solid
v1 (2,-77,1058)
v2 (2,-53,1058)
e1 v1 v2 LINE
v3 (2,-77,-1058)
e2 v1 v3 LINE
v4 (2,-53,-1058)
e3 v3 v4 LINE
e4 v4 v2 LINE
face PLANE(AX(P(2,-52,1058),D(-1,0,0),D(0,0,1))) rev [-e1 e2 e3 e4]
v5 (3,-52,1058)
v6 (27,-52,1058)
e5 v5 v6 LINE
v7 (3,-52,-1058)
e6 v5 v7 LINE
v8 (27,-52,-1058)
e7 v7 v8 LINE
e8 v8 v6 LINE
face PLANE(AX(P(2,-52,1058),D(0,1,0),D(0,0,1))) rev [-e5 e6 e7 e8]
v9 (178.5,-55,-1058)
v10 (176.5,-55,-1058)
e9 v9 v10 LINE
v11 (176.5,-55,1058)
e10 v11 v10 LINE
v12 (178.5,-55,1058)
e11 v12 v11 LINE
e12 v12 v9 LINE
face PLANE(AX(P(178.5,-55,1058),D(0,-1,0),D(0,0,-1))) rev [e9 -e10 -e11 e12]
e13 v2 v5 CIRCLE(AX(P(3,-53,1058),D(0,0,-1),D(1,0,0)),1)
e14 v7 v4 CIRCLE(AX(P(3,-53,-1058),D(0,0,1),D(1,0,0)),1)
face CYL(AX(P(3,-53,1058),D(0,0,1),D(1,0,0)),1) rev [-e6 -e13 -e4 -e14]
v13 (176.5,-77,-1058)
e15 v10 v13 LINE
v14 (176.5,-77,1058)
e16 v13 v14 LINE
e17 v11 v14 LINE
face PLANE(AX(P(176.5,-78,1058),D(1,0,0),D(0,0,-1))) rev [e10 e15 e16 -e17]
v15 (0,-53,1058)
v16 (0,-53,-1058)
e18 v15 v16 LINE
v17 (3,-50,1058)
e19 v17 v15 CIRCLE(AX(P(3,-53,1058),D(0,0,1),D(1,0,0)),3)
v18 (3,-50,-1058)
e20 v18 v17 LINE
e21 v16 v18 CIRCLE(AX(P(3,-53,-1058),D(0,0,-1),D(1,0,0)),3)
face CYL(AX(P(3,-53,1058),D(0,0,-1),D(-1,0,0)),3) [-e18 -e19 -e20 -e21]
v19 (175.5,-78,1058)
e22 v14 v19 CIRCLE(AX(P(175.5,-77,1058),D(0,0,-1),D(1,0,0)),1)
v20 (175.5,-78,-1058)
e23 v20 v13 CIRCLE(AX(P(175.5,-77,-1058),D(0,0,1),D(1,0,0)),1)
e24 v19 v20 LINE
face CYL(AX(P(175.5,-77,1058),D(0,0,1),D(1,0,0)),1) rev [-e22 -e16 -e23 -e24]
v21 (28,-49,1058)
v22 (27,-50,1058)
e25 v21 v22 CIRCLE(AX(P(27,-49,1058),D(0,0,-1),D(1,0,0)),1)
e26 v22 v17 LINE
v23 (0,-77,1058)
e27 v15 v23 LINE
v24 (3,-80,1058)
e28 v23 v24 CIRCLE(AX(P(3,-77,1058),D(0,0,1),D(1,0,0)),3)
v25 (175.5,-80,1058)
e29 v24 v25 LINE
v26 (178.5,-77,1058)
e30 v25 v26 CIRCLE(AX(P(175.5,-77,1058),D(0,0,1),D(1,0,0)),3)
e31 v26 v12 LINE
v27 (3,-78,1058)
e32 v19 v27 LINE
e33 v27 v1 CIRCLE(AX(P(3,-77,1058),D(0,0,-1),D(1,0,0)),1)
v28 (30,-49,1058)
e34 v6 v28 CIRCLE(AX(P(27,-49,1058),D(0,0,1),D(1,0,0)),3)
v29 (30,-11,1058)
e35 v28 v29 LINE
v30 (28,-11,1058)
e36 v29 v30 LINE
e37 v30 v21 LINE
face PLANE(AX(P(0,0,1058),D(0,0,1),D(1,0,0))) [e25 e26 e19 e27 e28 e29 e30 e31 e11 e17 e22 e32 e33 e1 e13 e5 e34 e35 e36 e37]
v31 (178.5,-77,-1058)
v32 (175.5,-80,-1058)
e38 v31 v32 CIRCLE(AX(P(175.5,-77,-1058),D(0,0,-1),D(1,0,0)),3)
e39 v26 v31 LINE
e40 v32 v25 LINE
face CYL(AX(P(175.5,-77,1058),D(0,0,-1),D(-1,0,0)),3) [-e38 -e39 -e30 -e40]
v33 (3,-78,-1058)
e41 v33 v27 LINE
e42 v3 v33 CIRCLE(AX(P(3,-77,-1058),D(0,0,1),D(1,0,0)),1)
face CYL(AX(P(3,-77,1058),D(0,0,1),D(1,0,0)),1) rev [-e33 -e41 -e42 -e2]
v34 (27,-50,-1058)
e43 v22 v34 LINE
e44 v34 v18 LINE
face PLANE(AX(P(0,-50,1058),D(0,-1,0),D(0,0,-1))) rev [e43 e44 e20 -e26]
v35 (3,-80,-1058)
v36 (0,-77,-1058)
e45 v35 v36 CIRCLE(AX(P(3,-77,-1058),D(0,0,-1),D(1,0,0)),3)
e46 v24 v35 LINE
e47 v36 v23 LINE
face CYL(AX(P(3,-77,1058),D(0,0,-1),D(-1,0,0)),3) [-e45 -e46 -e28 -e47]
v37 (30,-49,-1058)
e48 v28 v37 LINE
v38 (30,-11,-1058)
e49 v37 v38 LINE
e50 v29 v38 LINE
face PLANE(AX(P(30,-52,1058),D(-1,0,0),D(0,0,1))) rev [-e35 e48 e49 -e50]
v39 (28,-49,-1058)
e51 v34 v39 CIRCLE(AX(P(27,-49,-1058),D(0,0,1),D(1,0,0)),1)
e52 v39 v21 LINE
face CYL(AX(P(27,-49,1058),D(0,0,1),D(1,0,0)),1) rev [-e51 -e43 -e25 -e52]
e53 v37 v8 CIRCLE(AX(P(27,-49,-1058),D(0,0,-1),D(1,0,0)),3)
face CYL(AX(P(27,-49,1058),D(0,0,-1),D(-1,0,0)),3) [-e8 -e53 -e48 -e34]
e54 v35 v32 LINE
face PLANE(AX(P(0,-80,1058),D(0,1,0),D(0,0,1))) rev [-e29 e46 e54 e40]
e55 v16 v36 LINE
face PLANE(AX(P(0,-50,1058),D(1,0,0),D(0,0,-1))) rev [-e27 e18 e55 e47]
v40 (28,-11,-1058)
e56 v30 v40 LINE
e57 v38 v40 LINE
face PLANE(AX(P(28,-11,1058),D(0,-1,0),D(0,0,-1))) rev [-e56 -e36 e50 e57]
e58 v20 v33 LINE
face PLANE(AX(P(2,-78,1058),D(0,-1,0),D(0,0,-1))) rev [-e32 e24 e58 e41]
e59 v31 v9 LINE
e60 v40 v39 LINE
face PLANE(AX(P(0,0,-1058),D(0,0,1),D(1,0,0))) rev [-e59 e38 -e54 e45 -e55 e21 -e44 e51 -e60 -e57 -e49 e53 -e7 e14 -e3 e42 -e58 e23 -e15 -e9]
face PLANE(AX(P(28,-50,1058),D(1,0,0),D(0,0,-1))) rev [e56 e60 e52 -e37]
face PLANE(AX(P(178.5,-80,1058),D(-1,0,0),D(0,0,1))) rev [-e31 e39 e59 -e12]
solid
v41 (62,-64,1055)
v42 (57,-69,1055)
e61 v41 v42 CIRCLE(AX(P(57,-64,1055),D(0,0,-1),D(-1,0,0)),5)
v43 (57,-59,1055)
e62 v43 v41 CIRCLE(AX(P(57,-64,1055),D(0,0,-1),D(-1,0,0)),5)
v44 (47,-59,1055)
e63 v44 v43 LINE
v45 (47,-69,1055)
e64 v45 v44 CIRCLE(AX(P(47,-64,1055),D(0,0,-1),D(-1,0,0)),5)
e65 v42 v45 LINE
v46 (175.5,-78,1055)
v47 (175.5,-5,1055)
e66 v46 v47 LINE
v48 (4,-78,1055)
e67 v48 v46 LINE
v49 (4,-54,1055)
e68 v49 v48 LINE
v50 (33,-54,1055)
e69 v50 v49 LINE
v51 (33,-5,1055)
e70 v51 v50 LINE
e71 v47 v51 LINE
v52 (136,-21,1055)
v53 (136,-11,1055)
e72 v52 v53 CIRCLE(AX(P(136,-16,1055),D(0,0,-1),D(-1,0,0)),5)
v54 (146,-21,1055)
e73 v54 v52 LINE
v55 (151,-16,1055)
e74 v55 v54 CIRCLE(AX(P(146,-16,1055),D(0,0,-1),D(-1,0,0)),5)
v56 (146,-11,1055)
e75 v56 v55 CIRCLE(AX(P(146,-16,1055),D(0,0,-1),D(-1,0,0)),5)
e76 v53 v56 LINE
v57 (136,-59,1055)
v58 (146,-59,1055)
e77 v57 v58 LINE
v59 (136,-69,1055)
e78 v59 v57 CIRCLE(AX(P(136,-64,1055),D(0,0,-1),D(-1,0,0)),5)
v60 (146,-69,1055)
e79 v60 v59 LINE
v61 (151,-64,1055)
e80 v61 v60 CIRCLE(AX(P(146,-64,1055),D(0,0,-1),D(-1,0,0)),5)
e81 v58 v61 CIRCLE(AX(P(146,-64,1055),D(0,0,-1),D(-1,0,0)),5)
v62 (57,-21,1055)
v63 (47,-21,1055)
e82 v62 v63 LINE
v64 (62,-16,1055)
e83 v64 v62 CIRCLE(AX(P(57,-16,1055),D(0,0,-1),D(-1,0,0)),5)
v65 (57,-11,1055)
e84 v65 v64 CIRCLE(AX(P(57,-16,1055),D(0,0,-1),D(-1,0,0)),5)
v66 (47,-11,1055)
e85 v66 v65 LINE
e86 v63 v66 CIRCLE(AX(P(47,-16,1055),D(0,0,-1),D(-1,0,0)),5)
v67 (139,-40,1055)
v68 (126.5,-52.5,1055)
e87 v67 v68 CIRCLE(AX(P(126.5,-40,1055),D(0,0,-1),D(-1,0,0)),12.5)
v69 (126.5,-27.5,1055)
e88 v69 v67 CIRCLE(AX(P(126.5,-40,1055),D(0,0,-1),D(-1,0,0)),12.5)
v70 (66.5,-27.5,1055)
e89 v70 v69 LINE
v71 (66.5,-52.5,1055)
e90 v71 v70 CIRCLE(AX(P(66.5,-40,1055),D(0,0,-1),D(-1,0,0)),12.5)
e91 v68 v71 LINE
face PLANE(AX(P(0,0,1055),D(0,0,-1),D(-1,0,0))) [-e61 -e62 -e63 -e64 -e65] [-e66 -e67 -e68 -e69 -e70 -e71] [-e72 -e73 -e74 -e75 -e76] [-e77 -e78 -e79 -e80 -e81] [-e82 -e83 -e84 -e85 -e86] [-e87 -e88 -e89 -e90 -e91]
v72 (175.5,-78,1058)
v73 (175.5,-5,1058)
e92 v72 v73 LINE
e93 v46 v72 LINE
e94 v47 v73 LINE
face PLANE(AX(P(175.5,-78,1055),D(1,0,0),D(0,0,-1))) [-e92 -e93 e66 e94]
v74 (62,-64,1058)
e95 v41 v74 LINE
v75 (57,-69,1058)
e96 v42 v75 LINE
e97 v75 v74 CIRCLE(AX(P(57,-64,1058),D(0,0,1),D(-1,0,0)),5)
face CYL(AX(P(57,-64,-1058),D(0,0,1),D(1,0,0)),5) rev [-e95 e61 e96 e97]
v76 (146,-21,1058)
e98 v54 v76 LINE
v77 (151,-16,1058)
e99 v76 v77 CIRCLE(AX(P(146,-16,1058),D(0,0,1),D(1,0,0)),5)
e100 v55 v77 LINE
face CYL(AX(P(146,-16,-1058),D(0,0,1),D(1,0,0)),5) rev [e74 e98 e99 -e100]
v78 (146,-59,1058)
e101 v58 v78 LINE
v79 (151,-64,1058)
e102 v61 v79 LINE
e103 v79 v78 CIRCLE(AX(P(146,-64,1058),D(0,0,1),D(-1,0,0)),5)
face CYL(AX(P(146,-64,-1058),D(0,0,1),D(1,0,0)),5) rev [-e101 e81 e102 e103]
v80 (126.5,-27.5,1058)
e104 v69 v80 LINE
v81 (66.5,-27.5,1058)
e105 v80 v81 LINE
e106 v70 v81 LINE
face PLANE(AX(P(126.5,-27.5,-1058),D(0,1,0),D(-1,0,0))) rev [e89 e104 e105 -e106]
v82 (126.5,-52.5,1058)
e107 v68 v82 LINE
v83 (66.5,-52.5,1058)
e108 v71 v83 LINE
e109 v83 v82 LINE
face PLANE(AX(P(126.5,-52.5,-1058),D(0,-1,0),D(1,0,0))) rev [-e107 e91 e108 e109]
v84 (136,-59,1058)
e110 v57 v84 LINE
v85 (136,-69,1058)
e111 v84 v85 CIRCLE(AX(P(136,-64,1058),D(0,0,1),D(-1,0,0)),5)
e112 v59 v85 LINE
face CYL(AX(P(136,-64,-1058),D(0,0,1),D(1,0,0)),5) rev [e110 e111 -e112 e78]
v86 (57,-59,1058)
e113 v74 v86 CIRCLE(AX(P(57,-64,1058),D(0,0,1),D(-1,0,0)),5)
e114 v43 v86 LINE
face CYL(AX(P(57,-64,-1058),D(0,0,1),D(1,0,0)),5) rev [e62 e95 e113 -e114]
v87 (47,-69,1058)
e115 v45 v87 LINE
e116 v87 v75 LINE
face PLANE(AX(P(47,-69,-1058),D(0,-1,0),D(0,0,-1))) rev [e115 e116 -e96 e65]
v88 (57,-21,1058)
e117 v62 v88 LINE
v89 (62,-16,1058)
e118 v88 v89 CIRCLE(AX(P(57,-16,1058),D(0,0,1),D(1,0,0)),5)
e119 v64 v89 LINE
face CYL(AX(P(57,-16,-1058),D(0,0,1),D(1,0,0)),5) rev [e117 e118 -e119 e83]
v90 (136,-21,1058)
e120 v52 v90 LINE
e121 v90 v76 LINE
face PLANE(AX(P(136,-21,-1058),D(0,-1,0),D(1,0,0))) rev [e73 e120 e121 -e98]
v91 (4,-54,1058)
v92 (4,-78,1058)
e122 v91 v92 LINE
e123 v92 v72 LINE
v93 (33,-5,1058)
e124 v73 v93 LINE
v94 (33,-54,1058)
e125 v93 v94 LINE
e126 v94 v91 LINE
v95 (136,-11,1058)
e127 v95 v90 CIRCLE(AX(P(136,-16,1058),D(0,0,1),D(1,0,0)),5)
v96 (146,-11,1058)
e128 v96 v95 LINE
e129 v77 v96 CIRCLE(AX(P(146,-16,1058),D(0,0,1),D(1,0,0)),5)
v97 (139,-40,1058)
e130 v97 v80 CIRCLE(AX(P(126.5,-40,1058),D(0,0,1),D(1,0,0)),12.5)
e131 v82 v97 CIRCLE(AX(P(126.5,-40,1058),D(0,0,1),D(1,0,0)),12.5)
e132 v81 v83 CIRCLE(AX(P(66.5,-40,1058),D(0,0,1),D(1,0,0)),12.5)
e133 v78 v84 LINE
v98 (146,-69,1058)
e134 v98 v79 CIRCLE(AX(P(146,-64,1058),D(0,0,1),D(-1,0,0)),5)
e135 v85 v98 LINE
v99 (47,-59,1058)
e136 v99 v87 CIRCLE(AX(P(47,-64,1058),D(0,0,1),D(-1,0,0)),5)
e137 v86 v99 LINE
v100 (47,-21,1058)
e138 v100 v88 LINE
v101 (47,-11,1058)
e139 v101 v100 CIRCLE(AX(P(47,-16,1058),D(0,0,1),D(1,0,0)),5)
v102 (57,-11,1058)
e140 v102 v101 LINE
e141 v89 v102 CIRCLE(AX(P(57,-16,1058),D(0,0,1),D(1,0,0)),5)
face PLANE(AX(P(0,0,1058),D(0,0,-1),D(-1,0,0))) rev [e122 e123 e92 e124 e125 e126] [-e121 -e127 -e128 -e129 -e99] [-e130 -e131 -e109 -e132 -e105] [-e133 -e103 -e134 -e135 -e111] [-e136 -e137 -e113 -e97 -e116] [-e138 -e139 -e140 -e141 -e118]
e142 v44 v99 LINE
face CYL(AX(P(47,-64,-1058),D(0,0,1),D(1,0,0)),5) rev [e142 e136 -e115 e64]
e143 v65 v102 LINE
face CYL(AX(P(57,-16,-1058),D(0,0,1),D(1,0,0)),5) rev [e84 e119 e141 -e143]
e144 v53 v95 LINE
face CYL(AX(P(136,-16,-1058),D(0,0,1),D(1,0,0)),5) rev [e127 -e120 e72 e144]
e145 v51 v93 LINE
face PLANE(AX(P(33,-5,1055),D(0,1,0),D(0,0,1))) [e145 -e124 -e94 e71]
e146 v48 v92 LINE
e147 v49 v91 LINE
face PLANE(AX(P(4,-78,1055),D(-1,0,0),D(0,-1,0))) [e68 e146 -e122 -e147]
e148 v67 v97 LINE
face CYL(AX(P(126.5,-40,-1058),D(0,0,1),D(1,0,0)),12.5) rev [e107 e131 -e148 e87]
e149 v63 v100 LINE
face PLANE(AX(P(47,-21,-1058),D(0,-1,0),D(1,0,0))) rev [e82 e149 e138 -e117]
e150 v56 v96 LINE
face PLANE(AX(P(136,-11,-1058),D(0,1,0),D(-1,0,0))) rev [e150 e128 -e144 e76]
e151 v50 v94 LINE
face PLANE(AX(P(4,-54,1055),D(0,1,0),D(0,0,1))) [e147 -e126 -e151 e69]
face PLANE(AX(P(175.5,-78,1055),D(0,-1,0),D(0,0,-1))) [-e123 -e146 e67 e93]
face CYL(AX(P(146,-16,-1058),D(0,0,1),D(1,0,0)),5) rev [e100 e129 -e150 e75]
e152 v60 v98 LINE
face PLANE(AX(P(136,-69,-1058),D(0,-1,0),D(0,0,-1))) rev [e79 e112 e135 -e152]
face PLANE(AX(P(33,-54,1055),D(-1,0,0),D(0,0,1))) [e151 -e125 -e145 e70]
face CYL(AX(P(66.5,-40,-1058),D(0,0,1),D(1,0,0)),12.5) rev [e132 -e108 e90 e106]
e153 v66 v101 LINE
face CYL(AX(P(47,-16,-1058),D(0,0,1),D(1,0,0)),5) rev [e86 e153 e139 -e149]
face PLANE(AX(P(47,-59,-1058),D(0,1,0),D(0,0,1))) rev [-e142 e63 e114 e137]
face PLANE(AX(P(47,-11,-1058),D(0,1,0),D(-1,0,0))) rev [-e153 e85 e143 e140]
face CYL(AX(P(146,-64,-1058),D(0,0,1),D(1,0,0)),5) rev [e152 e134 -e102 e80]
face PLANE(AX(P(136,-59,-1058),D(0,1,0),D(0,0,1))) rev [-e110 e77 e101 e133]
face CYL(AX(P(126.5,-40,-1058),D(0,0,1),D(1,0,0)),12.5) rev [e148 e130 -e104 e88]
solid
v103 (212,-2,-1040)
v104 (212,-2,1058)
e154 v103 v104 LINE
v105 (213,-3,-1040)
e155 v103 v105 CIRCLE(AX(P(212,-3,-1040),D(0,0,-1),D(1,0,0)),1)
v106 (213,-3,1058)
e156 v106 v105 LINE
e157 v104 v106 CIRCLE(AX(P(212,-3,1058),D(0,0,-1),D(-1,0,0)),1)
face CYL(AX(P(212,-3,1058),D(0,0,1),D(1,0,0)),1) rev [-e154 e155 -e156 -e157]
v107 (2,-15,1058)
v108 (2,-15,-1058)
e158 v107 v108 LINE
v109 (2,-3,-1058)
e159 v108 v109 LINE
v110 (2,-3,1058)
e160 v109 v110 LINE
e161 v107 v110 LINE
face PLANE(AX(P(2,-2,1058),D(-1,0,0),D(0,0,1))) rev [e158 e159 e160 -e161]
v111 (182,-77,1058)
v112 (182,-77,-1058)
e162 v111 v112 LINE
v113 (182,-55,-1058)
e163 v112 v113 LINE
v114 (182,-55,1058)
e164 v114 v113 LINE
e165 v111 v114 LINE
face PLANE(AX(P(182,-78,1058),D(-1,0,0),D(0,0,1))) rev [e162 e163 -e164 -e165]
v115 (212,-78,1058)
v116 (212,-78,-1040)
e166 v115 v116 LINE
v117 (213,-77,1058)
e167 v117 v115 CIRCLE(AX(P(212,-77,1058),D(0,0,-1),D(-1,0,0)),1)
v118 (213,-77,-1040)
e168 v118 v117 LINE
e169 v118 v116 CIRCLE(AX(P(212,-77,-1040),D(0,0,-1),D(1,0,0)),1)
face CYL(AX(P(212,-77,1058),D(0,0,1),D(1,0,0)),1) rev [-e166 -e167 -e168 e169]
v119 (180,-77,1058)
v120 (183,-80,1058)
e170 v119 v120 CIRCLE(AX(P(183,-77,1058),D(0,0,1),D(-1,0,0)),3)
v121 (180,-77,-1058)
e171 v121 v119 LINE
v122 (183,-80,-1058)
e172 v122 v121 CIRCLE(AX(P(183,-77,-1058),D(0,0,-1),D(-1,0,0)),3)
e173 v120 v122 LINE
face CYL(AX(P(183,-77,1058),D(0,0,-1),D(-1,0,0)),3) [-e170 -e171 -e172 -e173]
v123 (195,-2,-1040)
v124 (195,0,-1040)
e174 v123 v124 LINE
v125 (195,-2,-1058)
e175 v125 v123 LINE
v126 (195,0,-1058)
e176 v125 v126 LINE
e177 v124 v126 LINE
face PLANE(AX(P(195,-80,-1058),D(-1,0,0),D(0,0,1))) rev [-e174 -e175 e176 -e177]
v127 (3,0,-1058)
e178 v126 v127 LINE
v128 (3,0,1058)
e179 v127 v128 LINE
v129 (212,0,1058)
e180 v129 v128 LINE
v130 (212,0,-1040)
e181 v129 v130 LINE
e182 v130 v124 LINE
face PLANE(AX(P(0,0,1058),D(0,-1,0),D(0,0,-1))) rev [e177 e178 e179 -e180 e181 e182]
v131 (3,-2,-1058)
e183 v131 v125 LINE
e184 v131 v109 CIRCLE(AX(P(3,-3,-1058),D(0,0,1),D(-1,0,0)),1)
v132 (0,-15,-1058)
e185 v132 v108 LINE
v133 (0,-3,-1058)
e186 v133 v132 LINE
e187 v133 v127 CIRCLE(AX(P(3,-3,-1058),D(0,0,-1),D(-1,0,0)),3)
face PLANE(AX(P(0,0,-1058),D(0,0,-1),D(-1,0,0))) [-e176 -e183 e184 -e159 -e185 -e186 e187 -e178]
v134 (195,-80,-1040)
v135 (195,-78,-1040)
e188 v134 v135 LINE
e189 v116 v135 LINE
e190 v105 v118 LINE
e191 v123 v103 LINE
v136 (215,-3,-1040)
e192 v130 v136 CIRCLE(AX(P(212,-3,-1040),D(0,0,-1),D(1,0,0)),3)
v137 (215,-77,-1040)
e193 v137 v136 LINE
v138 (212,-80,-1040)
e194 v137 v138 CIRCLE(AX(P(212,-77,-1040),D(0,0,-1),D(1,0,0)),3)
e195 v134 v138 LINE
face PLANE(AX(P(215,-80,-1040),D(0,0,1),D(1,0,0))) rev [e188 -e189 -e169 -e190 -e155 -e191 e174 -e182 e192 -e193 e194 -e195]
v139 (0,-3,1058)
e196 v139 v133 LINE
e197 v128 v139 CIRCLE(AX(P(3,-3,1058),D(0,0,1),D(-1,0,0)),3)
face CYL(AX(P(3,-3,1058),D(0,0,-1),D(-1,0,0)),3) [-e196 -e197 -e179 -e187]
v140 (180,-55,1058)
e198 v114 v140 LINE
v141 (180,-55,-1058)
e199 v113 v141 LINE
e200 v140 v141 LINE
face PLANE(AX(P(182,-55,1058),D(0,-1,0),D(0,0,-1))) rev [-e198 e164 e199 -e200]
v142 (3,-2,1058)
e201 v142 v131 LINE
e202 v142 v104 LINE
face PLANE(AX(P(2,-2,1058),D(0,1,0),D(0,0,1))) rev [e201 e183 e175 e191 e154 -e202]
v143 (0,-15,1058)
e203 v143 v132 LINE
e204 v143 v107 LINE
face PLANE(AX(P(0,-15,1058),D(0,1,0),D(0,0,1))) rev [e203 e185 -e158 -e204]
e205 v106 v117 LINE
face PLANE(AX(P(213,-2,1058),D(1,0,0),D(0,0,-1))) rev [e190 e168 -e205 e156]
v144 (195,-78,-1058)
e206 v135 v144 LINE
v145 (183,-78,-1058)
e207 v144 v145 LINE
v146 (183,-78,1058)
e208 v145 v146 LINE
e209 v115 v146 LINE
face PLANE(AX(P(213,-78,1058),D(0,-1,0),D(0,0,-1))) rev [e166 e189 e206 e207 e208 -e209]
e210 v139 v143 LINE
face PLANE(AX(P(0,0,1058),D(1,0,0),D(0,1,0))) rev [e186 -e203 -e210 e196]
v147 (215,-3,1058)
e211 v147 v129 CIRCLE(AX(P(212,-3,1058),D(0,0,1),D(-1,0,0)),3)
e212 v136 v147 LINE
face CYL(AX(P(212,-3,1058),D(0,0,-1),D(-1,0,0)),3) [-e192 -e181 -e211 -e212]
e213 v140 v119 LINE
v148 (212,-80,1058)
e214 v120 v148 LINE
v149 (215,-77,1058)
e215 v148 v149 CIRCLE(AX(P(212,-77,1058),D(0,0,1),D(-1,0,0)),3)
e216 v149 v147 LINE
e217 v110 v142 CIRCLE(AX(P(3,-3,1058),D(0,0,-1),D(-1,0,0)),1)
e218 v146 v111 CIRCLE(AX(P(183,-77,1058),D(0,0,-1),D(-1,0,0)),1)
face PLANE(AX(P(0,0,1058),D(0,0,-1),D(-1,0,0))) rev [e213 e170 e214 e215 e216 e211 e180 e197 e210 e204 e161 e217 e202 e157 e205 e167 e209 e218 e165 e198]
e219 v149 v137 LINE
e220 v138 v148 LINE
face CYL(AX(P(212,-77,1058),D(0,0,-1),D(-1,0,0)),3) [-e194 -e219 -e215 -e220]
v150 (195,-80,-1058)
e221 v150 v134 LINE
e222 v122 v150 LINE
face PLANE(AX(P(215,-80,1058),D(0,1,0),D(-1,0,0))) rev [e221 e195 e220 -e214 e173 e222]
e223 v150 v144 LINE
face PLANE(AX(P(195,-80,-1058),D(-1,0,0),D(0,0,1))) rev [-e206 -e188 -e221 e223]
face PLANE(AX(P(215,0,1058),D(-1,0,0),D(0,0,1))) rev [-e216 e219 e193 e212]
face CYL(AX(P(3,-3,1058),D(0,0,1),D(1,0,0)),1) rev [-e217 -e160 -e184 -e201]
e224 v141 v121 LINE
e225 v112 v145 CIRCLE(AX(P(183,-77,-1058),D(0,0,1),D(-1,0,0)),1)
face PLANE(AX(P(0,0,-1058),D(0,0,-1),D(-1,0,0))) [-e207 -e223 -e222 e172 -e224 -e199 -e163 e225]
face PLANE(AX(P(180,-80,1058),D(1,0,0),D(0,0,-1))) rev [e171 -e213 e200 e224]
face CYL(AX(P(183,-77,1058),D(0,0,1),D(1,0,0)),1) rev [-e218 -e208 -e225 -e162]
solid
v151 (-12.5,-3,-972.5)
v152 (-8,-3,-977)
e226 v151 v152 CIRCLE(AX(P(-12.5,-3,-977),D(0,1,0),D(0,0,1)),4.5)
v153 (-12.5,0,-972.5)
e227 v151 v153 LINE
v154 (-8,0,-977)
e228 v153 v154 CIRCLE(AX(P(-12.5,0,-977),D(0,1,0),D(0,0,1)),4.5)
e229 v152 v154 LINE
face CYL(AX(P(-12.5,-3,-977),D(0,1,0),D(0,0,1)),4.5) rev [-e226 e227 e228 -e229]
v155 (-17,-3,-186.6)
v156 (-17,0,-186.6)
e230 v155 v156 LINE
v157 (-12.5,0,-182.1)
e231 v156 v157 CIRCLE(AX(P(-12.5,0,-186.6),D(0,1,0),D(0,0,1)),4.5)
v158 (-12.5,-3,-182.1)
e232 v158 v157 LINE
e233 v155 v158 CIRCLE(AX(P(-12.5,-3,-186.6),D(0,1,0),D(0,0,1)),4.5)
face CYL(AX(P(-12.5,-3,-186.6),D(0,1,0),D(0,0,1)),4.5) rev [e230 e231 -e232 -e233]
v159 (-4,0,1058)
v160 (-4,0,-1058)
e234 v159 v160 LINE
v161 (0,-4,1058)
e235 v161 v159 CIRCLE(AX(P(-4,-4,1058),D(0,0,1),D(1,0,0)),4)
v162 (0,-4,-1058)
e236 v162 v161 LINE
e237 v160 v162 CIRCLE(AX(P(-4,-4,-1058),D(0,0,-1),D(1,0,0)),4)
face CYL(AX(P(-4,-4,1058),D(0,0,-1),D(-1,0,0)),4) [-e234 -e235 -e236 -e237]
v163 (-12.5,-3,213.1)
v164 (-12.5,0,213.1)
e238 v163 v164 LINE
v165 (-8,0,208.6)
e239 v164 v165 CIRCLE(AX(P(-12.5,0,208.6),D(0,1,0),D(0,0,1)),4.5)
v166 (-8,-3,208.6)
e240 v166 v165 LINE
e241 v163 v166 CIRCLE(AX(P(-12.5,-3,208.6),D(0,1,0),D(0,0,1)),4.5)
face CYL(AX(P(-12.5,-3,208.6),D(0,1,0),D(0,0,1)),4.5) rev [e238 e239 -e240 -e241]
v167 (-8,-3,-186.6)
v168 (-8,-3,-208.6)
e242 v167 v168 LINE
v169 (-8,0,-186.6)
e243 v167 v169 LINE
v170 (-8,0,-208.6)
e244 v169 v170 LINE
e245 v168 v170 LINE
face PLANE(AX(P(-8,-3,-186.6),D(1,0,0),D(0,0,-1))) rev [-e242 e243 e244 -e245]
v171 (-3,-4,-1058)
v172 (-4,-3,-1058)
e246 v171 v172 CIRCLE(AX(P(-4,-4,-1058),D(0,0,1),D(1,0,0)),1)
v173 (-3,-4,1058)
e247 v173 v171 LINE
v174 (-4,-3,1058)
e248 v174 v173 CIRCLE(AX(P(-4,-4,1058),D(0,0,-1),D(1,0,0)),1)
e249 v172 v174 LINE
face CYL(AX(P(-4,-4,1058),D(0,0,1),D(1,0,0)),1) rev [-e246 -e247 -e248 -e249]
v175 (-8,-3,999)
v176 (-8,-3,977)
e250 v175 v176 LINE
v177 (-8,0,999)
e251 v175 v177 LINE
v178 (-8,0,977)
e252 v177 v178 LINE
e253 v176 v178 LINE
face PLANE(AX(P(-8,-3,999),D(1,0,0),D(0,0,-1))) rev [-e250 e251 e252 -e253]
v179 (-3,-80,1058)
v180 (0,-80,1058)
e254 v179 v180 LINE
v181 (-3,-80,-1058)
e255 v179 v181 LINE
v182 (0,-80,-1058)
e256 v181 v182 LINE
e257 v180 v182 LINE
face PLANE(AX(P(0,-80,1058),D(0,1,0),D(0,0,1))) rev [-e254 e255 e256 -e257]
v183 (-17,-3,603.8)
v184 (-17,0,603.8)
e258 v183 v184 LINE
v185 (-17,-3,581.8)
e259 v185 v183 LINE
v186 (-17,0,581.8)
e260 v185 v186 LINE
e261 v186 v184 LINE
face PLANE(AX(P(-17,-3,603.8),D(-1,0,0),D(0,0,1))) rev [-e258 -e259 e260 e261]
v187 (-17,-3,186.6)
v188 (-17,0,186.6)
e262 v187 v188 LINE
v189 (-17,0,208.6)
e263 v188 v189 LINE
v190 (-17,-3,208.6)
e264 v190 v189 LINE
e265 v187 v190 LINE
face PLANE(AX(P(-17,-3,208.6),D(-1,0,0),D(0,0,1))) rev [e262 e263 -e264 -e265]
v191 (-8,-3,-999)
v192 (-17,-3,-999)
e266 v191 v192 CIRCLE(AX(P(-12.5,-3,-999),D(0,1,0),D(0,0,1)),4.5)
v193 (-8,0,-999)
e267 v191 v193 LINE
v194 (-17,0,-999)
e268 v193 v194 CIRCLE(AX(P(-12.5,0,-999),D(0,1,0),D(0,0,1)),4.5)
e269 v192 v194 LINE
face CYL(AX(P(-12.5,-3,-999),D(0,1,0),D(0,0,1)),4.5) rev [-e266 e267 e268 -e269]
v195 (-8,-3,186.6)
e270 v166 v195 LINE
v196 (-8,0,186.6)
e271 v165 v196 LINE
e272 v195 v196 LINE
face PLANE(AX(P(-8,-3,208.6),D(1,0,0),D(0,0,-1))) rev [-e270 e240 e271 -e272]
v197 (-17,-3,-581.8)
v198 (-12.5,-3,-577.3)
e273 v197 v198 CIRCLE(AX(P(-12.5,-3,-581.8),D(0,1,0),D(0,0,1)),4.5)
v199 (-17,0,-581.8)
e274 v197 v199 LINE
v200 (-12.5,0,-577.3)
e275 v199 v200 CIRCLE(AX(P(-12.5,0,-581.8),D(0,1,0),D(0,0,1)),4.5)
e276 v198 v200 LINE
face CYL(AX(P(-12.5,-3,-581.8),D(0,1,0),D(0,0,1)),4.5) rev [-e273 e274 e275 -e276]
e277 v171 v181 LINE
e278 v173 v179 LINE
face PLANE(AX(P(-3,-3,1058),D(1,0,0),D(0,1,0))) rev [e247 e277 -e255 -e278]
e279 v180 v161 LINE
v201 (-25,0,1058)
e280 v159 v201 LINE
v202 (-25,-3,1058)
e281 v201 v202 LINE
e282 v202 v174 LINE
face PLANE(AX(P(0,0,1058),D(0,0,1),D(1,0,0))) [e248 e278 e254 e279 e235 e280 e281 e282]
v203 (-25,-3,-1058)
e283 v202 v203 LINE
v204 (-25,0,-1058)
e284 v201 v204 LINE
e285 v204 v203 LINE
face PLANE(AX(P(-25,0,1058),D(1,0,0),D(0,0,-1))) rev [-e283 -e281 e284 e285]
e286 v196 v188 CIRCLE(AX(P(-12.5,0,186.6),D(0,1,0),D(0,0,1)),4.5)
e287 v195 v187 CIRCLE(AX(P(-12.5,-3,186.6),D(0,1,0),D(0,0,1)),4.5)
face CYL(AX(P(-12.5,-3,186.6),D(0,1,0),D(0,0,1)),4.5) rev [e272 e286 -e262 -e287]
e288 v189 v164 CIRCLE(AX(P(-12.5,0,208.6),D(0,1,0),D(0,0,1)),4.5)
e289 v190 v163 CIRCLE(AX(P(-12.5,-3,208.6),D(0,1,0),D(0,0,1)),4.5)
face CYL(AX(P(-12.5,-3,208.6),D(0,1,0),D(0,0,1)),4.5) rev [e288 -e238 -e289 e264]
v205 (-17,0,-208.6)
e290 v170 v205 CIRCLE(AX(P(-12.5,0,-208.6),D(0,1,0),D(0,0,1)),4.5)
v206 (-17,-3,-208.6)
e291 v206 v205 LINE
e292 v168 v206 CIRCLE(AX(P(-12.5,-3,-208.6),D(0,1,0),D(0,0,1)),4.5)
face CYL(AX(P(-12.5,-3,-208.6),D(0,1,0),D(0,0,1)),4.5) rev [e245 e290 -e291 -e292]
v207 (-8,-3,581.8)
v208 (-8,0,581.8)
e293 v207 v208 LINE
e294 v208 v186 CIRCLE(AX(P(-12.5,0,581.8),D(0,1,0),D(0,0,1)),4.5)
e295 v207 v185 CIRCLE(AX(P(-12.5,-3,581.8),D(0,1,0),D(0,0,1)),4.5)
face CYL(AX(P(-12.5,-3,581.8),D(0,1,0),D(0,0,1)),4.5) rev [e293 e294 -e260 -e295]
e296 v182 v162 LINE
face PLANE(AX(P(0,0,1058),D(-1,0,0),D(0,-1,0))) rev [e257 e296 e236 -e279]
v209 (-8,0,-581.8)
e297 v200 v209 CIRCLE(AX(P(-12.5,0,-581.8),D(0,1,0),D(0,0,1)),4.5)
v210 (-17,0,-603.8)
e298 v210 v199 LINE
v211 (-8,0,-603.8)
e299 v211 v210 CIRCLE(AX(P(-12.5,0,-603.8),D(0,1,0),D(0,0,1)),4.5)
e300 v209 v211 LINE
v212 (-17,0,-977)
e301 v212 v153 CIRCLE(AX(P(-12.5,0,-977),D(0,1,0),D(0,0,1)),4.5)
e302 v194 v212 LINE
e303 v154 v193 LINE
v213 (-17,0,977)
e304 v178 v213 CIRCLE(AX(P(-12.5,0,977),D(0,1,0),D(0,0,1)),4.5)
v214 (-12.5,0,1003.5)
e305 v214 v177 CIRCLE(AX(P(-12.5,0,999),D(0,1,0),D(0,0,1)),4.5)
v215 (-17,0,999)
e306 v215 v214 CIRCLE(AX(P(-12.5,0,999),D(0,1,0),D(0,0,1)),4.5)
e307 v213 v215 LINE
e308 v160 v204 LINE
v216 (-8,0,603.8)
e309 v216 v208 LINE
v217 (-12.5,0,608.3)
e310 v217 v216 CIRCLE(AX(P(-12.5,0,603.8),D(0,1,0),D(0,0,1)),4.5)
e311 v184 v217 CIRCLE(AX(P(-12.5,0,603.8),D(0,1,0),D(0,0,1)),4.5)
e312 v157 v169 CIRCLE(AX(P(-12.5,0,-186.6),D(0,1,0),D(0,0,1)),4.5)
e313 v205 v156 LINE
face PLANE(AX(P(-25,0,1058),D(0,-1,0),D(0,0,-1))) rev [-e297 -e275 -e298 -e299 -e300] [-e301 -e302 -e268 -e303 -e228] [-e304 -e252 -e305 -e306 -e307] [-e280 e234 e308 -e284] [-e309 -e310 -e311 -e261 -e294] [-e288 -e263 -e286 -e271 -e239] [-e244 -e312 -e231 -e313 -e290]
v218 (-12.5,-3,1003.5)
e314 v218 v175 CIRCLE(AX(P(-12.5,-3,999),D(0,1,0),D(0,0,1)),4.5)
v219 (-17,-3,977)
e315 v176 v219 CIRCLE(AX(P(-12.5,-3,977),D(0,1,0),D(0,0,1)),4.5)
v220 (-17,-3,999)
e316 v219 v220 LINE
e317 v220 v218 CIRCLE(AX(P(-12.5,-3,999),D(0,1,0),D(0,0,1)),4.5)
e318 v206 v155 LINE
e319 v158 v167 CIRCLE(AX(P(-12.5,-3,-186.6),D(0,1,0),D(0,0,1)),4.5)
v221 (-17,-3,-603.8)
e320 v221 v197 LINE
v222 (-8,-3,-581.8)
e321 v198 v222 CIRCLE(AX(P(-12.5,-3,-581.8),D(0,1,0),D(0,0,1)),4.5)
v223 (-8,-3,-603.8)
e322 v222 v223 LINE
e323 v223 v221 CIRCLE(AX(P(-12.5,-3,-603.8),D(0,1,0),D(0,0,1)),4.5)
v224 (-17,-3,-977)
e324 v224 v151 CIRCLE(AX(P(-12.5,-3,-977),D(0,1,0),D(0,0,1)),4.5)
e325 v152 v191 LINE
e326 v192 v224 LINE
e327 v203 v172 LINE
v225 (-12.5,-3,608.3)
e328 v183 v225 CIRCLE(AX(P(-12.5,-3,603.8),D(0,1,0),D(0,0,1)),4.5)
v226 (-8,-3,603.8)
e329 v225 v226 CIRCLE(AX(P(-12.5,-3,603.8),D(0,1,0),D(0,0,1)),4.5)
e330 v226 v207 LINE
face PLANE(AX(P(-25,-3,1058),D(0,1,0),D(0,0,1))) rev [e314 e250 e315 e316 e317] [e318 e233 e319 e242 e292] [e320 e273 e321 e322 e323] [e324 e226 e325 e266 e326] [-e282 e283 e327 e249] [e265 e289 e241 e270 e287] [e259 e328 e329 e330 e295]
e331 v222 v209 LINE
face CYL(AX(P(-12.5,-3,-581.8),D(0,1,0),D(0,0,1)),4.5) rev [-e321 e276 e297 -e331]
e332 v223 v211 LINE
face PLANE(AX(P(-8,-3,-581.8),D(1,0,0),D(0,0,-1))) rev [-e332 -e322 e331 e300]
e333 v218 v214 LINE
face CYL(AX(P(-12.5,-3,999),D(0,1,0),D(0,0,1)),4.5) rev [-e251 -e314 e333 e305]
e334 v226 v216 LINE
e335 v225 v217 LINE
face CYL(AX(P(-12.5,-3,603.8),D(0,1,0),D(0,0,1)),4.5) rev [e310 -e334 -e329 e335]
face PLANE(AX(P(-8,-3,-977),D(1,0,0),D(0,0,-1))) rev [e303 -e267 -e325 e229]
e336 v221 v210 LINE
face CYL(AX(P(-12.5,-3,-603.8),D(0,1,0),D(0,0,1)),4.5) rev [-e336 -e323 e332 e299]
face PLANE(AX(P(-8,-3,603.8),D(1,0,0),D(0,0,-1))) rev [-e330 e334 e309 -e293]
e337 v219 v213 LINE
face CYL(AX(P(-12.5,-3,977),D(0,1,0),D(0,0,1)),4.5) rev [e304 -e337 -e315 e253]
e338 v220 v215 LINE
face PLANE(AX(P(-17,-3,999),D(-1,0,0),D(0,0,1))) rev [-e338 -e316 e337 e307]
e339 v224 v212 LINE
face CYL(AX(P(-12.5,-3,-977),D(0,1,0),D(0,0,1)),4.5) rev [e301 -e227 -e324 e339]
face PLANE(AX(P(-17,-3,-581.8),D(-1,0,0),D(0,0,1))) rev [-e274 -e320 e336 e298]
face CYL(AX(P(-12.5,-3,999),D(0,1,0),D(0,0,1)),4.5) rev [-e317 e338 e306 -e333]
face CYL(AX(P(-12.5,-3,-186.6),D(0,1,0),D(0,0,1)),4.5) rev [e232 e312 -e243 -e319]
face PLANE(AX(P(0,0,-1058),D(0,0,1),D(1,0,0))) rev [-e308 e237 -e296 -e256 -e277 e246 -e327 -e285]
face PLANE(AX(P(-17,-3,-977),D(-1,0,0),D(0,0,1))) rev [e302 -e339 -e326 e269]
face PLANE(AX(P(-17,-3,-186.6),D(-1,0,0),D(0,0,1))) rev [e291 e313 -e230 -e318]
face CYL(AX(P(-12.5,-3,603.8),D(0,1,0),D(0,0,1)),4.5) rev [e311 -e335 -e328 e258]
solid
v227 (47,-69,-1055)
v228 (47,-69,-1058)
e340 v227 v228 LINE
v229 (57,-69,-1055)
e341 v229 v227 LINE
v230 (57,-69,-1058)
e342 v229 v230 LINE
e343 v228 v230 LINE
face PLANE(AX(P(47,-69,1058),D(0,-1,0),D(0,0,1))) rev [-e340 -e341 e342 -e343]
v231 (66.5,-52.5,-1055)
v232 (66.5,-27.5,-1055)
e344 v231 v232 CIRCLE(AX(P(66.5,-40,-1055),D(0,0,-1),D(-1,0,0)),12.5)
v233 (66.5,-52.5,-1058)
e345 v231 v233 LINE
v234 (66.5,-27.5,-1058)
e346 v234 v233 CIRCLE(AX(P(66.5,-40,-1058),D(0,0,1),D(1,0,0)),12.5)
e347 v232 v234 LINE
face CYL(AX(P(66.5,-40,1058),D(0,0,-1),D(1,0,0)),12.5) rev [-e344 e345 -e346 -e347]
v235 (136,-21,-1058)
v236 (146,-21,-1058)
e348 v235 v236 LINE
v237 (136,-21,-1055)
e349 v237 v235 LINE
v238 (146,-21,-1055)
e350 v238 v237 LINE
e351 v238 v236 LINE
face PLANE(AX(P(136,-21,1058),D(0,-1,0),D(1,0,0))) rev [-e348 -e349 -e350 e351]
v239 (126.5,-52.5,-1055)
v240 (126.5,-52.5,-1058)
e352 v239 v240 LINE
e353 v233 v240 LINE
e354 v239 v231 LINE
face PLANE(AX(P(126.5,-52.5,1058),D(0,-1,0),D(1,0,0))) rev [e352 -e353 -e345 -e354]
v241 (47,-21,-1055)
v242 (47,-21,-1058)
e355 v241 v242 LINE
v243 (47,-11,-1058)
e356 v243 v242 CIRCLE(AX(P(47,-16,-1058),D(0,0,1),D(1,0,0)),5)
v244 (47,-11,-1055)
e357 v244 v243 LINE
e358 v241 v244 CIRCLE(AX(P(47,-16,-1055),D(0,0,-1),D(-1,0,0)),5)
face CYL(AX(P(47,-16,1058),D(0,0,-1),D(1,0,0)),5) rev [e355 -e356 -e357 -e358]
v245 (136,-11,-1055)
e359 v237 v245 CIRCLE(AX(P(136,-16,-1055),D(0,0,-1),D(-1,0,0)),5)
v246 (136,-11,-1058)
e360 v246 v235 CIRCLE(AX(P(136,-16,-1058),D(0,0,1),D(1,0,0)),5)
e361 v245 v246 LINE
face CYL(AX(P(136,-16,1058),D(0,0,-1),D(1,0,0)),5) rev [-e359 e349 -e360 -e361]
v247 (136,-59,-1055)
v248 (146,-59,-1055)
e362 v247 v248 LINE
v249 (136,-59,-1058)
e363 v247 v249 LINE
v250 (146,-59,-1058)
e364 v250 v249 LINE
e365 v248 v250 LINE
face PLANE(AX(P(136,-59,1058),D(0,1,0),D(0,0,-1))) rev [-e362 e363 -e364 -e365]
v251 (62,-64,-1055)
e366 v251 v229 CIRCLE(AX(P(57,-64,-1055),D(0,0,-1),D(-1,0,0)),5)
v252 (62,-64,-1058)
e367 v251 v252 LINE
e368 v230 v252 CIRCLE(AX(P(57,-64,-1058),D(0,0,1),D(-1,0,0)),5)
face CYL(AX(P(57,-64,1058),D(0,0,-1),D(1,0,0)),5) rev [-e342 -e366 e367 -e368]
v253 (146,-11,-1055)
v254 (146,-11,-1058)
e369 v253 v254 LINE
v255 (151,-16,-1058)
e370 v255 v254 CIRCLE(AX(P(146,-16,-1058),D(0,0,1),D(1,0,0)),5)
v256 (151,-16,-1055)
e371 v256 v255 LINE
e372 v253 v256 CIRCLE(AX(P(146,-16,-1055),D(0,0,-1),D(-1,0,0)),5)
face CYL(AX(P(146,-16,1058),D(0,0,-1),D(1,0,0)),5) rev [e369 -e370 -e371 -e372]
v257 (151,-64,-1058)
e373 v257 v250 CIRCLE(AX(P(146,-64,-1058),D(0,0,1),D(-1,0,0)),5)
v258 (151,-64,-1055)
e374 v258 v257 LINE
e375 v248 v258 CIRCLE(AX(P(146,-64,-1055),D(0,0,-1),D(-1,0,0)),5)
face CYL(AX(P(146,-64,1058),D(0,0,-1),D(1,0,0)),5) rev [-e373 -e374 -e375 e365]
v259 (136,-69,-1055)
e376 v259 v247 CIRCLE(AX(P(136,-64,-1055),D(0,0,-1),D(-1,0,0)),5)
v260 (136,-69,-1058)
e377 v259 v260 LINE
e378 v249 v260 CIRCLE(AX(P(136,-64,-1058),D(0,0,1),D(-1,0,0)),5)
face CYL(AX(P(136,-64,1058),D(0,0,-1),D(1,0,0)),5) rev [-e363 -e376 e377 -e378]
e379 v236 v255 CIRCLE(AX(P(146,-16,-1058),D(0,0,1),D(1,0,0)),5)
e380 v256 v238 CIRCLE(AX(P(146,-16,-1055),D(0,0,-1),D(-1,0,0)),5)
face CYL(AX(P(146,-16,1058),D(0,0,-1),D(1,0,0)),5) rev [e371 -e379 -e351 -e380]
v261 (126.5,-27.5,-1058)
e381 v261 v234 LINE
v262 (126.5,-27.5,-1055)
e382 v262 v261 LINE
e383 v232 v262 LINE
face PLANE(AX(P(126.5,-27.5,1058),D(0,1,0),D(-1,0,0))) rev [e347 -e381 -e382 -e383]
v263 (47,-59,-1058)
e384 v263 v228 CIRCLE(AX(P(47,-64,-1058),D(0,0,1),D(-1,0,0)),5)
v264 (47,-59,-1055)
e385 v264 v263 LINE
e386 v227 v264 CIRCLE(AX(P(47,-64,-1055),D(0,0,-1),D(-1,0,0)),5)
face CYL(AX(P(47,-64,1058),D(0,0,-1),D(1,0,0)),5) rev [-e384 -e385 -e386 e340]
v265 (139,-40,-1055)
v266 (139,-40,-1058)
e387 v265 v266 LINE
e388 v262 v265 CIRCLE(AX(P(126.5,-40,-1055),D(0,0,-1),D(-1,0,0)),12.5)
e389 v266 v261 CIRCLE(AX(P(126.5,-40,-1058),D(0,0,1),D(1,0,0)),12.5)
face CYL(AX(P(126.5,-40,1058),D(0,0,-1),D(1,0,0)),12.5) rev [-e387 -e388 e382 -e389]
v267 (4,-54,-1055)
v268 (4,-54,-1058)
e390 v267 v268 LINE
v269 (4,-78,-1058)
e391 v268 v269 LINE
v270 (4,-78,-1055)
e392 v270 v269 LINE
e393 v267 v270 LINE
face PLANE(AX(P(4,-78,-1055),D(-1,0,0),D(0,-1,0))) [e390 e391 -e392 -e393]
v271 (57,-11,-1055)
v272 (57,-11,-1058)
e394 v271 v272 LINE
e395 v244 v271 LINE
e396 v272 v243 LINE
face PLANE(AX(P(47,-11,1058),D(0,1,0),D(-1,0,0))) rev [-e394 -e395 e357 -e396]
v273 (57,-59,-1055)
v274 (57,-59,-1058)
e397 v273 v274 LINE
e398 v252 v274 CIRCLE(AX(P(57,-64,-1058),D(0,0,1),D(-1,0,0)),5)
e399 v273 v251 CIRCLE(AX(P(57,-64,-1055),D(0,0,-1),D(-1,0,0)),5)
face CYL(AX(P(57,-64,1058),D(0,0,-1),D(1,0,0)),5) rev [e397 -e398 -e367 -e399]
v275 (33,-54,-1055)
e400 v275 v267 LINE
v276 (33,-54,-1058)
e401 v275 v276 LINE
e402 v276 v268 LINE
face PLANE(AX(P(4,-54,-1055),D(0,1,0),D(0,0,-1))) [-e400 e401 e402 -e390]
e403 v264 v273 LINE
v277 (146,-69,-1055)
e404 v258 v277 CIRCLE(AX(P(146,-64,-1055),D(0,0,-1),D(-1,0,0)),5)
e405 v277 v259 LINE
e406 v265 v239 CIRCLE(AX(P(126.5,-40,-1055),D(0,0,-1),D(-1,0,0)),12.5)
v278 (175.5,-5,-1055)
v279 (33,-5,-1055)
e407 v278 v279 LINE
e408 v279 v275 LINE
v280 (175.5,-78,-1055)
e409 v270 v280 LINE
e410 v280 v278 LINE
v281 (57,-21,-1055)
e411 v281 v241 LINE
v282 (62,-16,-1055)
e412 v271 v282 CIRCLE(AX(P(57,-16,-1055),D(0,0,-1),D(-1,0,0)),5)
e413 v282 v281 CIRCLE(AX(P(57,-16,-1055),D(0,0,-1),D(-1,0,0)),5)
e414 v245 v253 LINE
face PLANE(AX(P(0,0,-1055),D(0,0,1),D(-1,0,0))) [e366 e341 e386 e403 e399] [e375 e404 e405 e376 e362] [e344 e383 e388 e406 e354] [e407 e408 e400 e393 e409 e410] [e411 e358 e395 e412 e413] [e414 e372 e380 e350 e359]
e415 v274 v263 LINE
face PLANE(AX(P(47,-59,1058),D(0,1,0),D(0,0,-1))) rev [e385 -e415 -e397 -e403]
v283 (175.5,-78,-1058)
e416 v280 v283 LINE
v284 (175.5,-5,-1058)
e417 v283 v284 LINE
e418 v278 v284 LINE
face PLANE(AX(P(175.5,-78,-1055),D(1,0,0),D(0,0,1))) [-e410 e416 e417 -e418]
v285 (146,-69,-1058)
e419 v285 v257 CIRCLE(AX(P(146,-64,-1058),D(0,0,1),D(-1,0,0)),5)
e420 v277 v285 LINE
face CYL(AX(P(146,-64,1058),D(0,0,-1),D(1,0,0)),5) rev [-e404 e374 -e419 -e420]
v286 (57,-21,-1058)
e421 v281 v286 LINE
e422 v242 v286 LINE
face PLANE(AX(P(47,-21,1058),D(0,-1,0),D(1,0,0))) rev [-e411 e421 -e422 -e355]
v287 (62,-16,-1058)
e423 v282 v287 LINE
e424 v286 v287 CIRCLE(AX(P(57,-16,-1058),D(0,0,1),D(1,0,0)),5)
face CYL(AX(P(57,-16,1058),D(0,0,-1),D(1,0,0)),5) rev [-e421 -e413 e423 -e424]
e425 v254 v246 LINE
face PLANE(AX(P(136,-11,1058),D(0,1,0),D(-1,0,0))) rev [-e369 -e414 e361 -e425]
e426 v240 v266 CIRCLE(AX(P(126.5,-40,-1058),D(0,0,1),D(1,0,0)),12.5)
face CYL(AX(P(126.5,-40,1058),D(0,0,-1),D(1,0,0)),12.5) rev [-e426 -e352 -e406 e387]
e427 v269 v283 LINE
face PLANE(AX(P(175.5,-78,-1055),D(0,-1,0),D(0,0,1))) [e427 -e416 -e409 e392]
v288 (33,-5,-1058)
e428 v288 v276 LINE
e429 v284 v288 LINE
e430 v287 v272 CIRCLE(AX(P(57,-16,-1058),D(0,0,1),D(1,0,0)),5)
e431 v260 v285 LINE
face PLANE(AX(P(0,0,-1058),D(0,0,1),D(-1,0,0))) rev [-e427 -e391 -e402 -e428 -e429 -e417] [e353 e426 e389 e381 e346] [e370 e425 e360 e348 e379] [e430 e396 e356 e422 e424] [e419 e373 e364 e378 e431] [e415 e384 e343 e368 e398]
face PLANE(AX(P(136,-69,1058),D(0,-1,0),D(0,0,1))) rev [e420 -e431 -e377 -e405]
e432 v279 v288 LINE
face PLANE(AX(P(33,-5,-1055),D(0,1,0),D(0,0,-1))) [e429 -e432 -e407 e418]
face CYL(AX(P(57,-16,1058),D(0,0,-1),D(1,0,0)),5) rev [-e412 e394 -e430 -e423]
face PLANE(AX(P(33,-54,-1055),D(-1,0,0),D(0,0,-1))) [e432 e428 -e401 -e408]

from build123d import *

# Parameters (mm, degrees)
EXTRUDE_1_DEPTH             = 1058
EXTRUDE_2_DEPTH             = 1058
EXTRUDE_2_2_DEPTH           = 1058
EXTRUDE_3_DEPTH             = 3
FILLET_1_R                  = 4
FILLET_2_R                  = 1
FILLET_3_R                  = 1
FILLET_4_R                  = 1
FILLET_5_R                  = 3
FILLET_6_R                  = 3
CUT_EXTRUDE_1_DEPTH         = 2129.398693854
CUT_EXTRUDE_3493_DEPTH      = 3
CUT_EXTRUDE_3714_DEPTH      = 1083.584407795
CUT_EXTRUDE_3714_DEPTH_BACK = 1083.584407795
SKETCH_6_W                  = 20
SKETCH_6_H                  = 18


with BuildPart() as part:
    # 草图1 → 凸台-拉伸1 (new, symmetric)
    with BuildSketch(Plane.XY):
        Polygon((-25, 0), (0, 0), (0, -80), (-3, -80), (-3, -3), (-25, -3), align=None)
    extrude(amount=EXTRUDE_1_DEPTH, both=True)

    # 圆角1
    fillet_1_edges = [part.edges().sort_by_distance(p)[0] for p in [
        (0, 0, 0),
    ]]
    fillet(fillet_1_edges, radius=FILLET_1_R)

    # 圆角2
    fillet_2_edges = [part.edges().sort_by_distance(p)[0] for p in [
        (-3, -3, 0),
    ]]
    fillet(fillet_2_edges, radius=FILLET_2_R)

    # 草图7 → Cut-Extrude 3493 (cut)
    with BuildSketch(Plane(origin=(0, 0, 0), x_dir=(1, 0, 0), z_dir=(0, 1, 0))):
        with BuildLine():
            Line((-17, 977), (-17, 999))
            ThreePointArc((-17, 999), (-12.5, 1003.5), (-8, 999))
            Line((-8, 999), (-8, 977))
            ThreePointArc((-8, 977), (-12.5, 972.5), (-17, 977))
        make_face()
        with BuildLine():
            Line((-17, 581.8), (-17, 603.8))
            ThreePointArc((-17, 603.8), (-12.5, 608.3), (-8, 603.8))
            Line((-8, 603.8), (-8, 581.8))
            ThreePointArc((-8, 581.8), (-12.5, 577.3), (-17, 581.8))
        make_face()
        with BuildLine():
            Line((-17, 186.6), (-17, 208.6))
            ThreePointArc((-17, 208.6), (-12.5, 213.1), (-8, 208.6))
            Line((-8, 208.6), (-8, 186.6))
            ThreePointArc((-8, 186.6), (-12.5, 182.1), (-17, 186.6))
        make_face()
        with BuildLine():
            Line((-17, -208.6), (-17, -186.6))
            ThreePointArc((-17, -186.6), (-12.5, -182.1), (-8, -186.6))
            Line((-8, -186.6), (-8, -208.6))
            ThreePointArc((-8, -208.6), (-12.5, -213.1), (-17, -208.6))
        make_face()
        with BuildLine():
            Line((-17, -603.8), (-17, -581.8))
            ThreePointArc((-17, -581.8), (-12.5, -577.3), (-8, -581.8))
            Line((-8, -581.8), (-8, -603.8))
            ThreePointArc((-8, -603.8), (-12.5, -608.3), (-17, -603.8))
        make_face()
        with BuildLine():
            Line((-17, -999), (-17, -977))
            ThreePointArc((-17, -977), (-12.5, -972.5), (-8, -977))
            Line((-8, -977), (-8, -999))
            ThreePointArc((-8, -999), (-12.5, -1003.5), (-17, -999))
        make_face()
    extrude(amount=-CUT_EXTRUDE_3493_DEPTH, mode=Mode.SUBTRACT)


with BuildPart() as body_2:
    # 草图2 → 凸台-拉伸2 (new, symmetric)
    with BuildSketch(Plane.XY):
        Polygon((0, 0), (0, -15), (2, -15), (2, -2), (213, -2), (213, -78), (182, -78), (182, -55), (180, -55), (180, -80), (215, -80), (215, 0), align=None)
    extrude(amount=EXTRUDE_2_DEPTH, both=True)

    # 圆角3
    fillet_3_edges = [body_2.edges().sort_by_distance(p)[0] for p in [
        (182, -78, 0),
        (213, -78, 0),
        (213, -2, 0),
        (2, -2, 0),
    ]]
    fillet(fillet_3_edges, radius=FILLET_3_R)

    # 圆角5
    fillet_5_edges = [body_2.edges().sort_by_distance(p)[0] for p in [
        (215, 0, 0),
        (215, -80, 0),
        (180, -80, 0),
        (0, 0, 0),
    ]]
    fillet(fillet_5_edges, radius=FILLET_5_R)

    # 草图6 → Cut-Extrude 3714 (cut, two sides: drawn at the far end of the back side and taken through both)
    with BuildSketch(Plane(origin=(0, 0, 0), x_dir=(1, 0, 0), z_dir=(0, 1, 0)).offset(-CUT_EXTRUDE_3714_DEPTH_BACK)):
        with Locations((205, 1049)):
            Rectangle(SKETCH_6_W, SKETCH_6_H)
    extrude(amount=CUT_EXTRUDE_3714_DEPTH + CUT_EXTRUDE_3714_DEPTH_BACK, mode=Mode.SUBTRACT)


with BuildPart() as body_3:
    # 草图2 → Extrude 2 2 (new, symmetric)
    with BuildSketch(Plane.XY):
        Polygon((0, -50), (0, -80), (178.5, -80), (178.5, -55), (176.5, -55), (176.5, -78), (2, -78), (2, -52), (30, -52), (30, -11), (28, -11), (28, -50), align=None)
    extrude(amount=EXTRUDE_2_2_DEPTH, both=True)

    # 圆角4
    fillet_4_edges = [body_3.edges().sort_by_distance(p)[0] for p in [
        (28, -50, 0),
        (2, -52, 0),
        (2, -78, 0),
        (176.5, -78, 0),
    ]]
    fillet(fillet_4_edges, radius=FILLET_4_R)

    # 圆角6
    fillet_6_edges = [body_3.edges().sort_by_distance(p)[0] for p in [
        (30, -52, 0),
        (178.5, -80, 0),
        (0, -80, 0),
        (0, -50, 0),
    ]]
    fillet(fillet_6_edges, radius=FILLET_6_R)


with BuildPart() as body_4:
    # 草图3 → 凸台-拉伸3 (new body)
    with BuildSketch(Plane.XY.offset(1058)):
        Polygon((175.5, -78), (175.5, -5), (33, -5), (33, -54), (4, -54), (4, -78), align=None)
    extrude(amount=-EXTRUDE_3_DEPTH)

    # 草图5 → 切除-拉伸1 (cut, through all)
    with BuildSketch(Plane.XY.offset(1058)):
        with BuildLine():
            Line((47, -11), (57, -11))
            ThreePointArc((57, -11), (62, -16), (57, -21))
            Line((57, -21), (47, -21))
            ThreePointArc((47, -21), (42, -16), (47, -11))
        make_face()
        with BuildLine():
            Line((47, -69), (57, -69))
            ThreePointArc((57, -69), (62, -64), (57, -59))
            Line((57, -59), (47, -59))
            ThreePointArc((47, -59), (42, -64), (47, -69))
        make_face()
        with BuildLine():
            Line((136, -11), (146, -11))
            ThreePointArc((146, -11), (151, -16), (146, -21))
            Line((146, -21), (136, -21))
            ThreePointArc((136, -21), (131, -16), (136, -11))
        make_face()
        with BuildLine():
            Line((136, -69), (146, -69))
            ThreePointArc((146, -69), (151, -64), (146, -59))
            Line((146, -59), (136, -59))
            ThreePointArc((136, -59), (131, -64), (136, -69))
        make_face()
        with BuildLine():
            Line((126.5, -52.5), (66.5, -52.5))
            ThreePointArc((66.5, -52.5), (54, -40), (66.5, -27.5))
            Line((66.5, -27.5), (126.5, -27.5))
            ThreePointArc((126.5, -27.5), (139, -40), (126.5, -52.5))
        make_face()
    extrude(amount=-CUT_EXTRUDE_1_DEPTH, mode=Mode.SUBTRACT)


with BuildPart() as body_5:
    # 镜向1: mirrored copy
    add(body_4.part.mirror(Plane.XY))


solid = Compound([part.part, body_2.part, body_3.part, body_4.part, body_5.part])
